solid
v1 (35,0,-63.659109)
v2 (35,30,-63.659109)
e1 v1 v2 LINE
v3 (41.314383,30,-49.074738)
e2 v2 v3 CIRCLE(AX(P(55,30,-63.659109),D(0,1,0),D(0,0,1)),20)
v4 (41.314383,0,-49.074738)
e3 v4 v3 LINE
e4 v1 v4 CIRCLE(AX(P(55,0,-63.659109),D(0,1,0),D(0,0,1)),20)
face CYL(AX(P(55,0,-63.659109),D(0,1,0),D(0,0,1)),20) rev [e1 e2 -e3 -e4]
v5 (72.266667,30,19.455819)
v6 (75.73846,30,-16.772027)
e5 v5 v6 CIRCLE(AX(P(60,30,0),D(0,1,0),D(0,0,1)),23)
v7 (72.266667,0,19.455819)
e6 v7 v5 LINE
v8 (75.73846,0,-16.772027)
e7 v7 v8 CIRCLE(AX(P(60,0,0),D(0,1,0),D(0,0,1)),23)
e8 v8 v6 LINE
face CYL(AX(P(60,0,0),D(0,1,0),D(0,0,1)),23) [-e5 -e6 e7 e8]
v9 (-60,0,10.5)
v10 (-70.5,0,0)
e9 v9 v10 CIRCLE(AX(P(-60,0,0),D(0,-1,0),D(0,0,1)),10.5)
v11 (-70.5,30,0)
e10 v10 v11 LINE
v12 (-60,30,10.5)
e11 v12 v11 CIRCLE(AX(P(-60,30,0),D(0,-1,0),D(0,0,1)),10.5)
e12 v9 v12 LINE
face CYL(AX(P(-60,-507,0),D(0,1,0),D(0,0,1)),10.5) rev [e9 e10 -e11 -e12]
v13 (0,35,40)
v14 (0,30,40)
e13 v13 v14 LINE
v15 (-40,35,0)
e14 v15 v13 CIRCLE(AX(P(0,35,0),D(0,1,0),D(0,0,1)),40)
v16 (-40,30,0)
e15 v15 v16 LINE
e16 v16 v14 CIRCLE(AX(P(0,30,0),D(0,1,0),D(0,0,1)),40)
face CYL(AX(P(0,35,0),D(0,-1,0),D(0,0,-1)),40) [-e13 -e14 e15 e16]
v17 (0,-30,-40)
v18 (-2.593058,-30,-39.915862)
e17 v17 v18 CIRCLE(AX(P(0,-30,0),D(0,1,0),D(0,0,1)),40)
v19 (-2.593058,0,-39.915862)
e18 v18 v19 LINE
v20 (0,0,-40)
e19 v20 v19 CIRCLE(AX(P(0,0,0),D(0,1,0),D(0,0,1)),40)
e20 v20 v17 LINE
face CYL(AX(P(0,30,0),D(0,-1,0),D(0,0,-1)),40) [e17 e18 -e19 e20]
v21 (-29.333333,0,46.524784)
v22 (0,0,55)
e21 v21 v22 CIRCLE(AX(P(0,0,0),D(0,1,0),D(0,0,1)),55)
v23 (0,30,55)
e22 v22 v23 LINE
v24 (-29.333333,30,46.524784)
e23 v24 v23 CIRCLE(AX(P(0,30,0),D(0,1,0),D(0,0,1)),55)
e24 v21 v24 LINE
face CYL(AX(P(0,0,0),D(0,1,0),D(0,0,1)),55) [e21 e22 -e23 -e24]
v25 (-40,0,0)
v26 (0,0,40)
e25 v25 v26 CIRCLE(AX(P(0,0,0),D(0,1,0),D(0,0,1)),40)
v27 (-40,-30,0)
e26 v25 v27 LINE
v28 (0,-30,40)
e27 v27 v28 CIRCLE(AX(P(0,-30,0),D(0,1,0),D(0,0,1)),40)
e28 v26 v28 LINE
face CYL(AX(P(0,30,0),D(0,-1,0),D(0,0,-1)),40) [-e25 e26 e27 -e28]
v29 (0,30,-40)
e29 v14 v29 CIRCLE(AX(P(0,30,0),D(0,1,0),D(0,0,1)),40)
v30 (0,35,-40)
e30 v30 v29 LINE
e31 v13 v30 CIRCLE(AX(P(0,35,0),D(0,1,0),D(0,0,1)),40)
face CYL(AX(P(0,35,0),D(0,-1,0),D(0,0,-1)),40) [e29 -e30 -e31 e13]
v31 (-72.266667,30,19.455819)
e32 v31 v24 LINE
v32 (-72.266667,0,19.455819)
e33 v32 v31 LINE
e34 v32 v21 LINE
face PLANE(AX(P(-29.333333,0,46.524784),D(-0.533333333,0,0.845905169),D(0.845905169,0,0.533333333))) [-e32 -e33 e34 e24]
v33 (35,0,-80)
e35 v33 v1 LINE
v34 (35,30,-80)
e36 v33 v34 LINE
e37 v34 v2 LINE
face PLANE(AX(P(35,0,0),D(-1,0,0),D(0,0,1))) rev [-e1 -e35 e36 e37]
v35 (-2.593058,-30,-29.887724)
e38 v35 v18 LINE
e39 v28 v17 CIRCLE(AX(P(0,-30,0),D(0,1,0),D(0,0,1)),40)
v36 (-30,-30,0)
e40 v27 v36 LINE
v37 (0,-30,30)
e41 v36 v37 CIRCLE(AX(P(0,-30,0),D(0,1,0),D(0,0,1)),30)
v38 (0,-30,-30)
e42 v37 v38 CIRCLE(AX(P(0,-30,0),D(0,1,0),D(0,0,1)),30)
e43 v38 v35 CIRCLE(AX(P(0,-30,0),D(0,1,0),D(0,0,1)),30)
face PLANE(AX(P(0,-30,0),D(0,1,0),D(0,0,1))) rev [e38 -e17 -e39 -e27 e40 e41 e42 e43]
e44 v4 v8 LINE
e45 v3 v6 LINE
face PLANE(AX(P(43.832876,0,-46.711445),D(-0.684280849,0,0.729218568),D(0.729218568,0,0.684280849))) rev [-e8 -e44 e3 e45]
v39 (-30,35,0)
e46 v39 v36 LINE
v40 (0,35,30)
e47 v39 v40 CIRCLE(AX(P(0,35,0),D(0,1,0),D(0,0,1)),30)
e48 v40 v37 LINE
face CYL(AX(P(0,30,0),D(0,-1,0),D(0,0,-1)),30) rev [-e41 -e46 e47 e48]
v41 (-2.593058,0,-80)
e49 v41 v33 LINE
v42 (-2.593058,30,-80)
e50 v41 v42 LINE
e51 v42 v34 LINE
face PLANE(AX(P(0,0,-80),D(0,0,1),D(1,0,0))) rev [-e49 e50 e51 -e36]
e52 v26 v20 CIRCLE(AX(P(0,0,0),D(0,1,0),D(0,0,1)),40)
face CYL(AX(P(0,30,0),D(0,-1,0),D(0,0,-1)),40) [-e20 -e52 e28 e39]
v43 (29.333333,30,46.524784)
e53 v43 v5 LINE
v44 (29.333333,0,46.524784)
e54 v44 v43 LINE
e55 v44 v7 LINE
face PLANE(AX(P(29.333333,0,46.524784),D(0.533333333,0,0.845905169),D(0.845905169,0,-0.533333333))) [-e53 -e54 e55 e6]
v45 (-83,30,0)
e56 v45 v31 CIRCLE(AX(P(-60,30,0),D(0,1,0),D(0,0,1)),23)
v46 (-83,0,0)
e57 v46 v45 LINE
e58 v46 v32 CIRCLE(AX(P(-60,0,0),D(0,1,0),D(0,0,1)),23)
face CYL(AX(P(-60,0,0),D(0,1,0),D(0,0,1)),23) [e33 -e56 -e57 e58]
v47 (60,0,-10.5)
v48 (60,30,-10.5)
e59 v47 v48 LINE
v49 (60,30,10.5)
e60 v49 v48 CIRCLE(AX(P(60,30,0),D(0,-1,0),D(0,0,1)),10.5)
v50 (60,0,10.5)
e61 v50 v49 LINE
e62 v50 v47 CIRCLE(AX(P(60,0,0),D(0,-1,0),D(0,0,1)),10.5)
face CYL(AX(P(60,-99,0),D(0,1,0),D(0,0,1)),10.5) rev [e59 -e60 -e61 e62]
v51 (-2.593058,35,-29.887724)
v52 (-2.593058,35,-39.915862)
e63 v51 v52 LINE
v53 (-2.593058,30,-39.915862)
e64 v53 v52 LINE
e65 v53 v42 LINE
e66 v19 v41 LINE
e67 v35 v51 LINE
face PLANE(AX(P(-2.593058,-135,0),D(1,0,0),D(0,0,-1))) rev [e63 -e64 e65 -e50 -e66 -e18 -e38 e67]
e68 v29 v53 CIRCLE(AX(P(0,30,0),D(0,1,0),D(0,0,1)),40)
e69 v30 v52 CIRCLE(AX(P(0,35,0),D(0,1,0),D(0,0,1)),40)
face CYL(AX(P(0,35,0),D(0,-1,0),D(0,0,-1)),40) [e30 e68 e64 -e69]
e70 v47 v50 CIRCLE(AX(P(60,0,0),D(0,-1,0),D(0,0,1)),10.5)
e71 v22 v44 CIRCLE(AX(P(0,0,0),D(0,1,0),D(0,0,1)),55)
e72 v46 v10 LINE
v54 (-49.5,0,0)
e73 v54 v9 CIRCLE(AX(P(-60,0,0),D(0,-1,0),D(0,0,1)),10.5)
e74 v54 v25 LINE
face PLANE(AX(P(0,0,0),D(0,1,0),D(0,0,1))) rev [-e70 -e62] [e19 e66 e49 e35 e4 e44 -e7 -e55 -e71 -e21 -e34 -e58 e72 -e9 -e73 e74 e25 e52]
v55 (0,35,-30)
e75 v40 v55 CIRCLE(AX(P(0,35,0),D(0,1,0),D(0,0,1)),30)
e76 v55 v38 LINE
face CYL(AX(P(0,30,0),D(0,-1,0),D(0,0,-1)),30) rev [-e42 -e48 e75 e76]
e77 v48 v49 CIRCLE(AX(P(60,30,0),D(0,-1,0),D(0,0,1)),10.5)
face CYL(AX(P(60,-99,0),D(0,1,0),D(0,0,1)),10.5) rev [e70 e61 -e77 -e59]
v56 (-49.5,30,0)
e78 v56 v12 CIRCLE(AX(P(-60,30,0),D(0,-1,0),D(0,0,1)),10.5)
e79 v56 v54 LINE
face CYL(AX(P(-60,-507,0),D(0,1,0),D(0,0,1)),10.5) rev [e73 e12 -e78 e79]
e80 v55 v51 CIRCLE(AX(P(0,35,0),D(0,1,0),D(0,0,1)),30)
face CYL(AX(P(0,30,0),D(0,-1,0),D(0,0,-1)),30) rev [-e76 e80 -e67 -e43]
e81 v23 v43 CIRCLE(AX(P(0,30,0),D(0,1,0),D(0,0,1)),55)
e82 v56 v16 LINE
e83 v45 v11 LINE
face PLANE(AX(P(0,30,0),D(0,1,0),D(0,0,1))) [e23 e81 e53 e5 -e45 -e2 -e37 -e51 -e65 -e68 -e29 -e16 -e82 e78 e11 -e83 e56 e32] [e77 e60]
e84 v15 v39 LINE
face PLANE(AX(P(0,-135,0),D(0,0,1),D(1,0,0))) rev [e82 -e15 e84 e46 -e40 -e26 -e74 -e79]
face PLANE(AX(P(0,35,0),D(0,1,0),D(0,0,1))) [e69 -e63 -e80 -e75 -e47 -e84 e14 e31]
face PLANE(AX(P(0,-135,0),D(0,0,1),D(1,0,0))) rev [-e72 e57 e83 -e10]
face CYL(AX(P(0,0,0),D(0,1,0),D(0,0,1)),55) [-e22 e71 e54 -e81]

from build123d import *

# Parameters (mm, degrees)
HUB_TUBE_SKETCH_R        = 40
HUB_TUBE_SKETCH_R_2      = 30
HUB_TUBE_80_DEPTH        = 30
FLANGE_30MM_DEPTH        = 30
COLLAR_SKETCH_R          = 40
COLLAR_SKETCH_R_2        = 30
COLLAR_80_X5_DEPTH       = 5
SIDE_SLOT_CUT_DEPTH      = 135
SIDE_SLOT_CUT_DEPTH_BACK = 140
CUT_21_A_DEPTH           = 99
CUT_21_A_DEPTH_BACK      = 159
CUT_21_A_SKETCH_R        = 10.5
CUT_21_B_DEPTH           = 507
CUT_21_B_DEPTH_BACK      = 405
CUT_21_B_SKETCH_R        = 10.5


with BuildPart() as part:
    # Hub Tube Sketch → Hub Tube Ø80 (new, symmetric)
    with BuildSketch(Plane(origin=(0, 0, 0), x_dir=(1, 0, 0), z_dir=(0, 1, 0))):
        with Locations(Location((0, 0, 0), (0, 0, 270))):
            Circle(HUB_TUBE_SKETCH_R)
        with Locations(Location((0, 0, 0), (0, 0, 270))):
            Circle(HUB_TUBE_SKETCH_R_2, mode=Mode.SUBTRACT)
    extrude(amount=HUB_TUBE_80_DEPTH, both=True)

    # Flange Profile Sketch → Flange 30mm (add)
    with BuildSketch(Plane(origin=(0, 30, 0), x_dir=(1, 0, 0), z_dir=(0, 1, 0))):
        with BuildLine():
            ThreePointArc((-75.738459529, 16.772027059), (-82.895108188, -2.194087755), (-72.266666667, -19.455818895))
            Line((-72.266666667, -19.455818895), (-29.333333333, -46.524784315))
            ThreePointArc((-29.333333333, -46.524784315), (0, -55), (29.333333333, -46.524784315))
            Line((29.333333333, -46.524784315), (72.266666667, -19.455818895))
            ThreePointArc((72.266666667, -19.455818895), (82.895108188, -2.194087755), (75.738459529, 16.772027059))
            Line((75.738459529, 16.772027059), (41.314383018, 49.074737583))
            ThreePointArc((41.314383018, 49.074737583), (36.646358132, 55.712799721), (35, 63.659108939))
            Line((35, 63.659108939), (35, 80))
            Line((35, 80), (-35, 80))
            Line((-35, 80), (-35, 63.659108939))
            ThreePointArc((-35, 63.659108939), (-36.646358132, 55.712799721), (-41.314383018, 49.074737583))
            Line((-41.314383018, 49.074737583), (-75.738459529, 16.772027059))
        make_face()
        with BuildLine():
            ThreePointArc((40, 0), (-28.284271247, -28.284271247), (0, 40))
            ThreePointArc((0, 40), (28.284271247, 28.284271247), (40, 0))
        make_face(mode=Mode.SUBTRACT)
    extrude(amount=-FLANGE_30MM_DEPTH)

    # Collar Sketch → Collar Ø80 x5 (add)
    with BuildSketch(Plane(origin=(0, 30, 0), x_dir=(1, 0, 0), z_dir=(0, 1, 0))):
        with Locations(Location((0, 0, 0), (0, 0, 270))):
            Circle(COLLAR_SKETCH_R)
        with Locations(Location((0, 0, 0), (0, 0, 270))):
            Circle(COLLAR_SKETCH_R_2, mode=Mode.SUBTRACT)
    extrude(amount=COLLAR_80_X5_DEPTH)

    # Side Slot Sketch → Side Slot Cut (cut, two sides: drawn at the far end of the back side and taken through both)
    with BuildSketch(Plane.XZ.offset(-SIDE_SLOT_CUT_DEPTH_BACK)):
        Polygon((-109.161413969, 0), (-2.593057922, 0), (-2.593057922, -87.129471891), (-109.161413969, -88.900340716), align=None)
    extrude(amount=SIDE_SLOT_CUT_DEPTH + SIDE_SLOT_CUT_DEPTH_BACK, mode=Mode.SUBTRACT)

    # Cut Ø21 A Sketch → Cut Ø21 A (cut, two sides: drawn at the far end of the back side and taken through both)
    with BuildSketch(Plane.XZ.offset(-CUT_21_A_DEPTH_BACK)):
        with Locations(Location((60, 0, 0), (0, 0, 90))):
            Circle(CUT_21_A_SKETCH_R)
    extrude(amount=CUT_21_A_DEPTH + CUT_21_A_DEPTH_BACK, mode=Mode.SUBTRACT)

    # Cut Ø21 B Sketch → Cut Ø21 B (cut, two sides: drawn at the far end of the back side and taken through both)
    with BuildSketch(Plane.XZ.offset(-CUT_21_B_DEPTH_BACK)):
        with Locations((-60, 0)):
            Circle(CUT_21_B_SKETCH_R)
    extrude(amount=CUT_21_B_DEPTH + CUT_21_B_DEPTH_BACK, mode=Mode.SUBTRACT)


solid = part.part
